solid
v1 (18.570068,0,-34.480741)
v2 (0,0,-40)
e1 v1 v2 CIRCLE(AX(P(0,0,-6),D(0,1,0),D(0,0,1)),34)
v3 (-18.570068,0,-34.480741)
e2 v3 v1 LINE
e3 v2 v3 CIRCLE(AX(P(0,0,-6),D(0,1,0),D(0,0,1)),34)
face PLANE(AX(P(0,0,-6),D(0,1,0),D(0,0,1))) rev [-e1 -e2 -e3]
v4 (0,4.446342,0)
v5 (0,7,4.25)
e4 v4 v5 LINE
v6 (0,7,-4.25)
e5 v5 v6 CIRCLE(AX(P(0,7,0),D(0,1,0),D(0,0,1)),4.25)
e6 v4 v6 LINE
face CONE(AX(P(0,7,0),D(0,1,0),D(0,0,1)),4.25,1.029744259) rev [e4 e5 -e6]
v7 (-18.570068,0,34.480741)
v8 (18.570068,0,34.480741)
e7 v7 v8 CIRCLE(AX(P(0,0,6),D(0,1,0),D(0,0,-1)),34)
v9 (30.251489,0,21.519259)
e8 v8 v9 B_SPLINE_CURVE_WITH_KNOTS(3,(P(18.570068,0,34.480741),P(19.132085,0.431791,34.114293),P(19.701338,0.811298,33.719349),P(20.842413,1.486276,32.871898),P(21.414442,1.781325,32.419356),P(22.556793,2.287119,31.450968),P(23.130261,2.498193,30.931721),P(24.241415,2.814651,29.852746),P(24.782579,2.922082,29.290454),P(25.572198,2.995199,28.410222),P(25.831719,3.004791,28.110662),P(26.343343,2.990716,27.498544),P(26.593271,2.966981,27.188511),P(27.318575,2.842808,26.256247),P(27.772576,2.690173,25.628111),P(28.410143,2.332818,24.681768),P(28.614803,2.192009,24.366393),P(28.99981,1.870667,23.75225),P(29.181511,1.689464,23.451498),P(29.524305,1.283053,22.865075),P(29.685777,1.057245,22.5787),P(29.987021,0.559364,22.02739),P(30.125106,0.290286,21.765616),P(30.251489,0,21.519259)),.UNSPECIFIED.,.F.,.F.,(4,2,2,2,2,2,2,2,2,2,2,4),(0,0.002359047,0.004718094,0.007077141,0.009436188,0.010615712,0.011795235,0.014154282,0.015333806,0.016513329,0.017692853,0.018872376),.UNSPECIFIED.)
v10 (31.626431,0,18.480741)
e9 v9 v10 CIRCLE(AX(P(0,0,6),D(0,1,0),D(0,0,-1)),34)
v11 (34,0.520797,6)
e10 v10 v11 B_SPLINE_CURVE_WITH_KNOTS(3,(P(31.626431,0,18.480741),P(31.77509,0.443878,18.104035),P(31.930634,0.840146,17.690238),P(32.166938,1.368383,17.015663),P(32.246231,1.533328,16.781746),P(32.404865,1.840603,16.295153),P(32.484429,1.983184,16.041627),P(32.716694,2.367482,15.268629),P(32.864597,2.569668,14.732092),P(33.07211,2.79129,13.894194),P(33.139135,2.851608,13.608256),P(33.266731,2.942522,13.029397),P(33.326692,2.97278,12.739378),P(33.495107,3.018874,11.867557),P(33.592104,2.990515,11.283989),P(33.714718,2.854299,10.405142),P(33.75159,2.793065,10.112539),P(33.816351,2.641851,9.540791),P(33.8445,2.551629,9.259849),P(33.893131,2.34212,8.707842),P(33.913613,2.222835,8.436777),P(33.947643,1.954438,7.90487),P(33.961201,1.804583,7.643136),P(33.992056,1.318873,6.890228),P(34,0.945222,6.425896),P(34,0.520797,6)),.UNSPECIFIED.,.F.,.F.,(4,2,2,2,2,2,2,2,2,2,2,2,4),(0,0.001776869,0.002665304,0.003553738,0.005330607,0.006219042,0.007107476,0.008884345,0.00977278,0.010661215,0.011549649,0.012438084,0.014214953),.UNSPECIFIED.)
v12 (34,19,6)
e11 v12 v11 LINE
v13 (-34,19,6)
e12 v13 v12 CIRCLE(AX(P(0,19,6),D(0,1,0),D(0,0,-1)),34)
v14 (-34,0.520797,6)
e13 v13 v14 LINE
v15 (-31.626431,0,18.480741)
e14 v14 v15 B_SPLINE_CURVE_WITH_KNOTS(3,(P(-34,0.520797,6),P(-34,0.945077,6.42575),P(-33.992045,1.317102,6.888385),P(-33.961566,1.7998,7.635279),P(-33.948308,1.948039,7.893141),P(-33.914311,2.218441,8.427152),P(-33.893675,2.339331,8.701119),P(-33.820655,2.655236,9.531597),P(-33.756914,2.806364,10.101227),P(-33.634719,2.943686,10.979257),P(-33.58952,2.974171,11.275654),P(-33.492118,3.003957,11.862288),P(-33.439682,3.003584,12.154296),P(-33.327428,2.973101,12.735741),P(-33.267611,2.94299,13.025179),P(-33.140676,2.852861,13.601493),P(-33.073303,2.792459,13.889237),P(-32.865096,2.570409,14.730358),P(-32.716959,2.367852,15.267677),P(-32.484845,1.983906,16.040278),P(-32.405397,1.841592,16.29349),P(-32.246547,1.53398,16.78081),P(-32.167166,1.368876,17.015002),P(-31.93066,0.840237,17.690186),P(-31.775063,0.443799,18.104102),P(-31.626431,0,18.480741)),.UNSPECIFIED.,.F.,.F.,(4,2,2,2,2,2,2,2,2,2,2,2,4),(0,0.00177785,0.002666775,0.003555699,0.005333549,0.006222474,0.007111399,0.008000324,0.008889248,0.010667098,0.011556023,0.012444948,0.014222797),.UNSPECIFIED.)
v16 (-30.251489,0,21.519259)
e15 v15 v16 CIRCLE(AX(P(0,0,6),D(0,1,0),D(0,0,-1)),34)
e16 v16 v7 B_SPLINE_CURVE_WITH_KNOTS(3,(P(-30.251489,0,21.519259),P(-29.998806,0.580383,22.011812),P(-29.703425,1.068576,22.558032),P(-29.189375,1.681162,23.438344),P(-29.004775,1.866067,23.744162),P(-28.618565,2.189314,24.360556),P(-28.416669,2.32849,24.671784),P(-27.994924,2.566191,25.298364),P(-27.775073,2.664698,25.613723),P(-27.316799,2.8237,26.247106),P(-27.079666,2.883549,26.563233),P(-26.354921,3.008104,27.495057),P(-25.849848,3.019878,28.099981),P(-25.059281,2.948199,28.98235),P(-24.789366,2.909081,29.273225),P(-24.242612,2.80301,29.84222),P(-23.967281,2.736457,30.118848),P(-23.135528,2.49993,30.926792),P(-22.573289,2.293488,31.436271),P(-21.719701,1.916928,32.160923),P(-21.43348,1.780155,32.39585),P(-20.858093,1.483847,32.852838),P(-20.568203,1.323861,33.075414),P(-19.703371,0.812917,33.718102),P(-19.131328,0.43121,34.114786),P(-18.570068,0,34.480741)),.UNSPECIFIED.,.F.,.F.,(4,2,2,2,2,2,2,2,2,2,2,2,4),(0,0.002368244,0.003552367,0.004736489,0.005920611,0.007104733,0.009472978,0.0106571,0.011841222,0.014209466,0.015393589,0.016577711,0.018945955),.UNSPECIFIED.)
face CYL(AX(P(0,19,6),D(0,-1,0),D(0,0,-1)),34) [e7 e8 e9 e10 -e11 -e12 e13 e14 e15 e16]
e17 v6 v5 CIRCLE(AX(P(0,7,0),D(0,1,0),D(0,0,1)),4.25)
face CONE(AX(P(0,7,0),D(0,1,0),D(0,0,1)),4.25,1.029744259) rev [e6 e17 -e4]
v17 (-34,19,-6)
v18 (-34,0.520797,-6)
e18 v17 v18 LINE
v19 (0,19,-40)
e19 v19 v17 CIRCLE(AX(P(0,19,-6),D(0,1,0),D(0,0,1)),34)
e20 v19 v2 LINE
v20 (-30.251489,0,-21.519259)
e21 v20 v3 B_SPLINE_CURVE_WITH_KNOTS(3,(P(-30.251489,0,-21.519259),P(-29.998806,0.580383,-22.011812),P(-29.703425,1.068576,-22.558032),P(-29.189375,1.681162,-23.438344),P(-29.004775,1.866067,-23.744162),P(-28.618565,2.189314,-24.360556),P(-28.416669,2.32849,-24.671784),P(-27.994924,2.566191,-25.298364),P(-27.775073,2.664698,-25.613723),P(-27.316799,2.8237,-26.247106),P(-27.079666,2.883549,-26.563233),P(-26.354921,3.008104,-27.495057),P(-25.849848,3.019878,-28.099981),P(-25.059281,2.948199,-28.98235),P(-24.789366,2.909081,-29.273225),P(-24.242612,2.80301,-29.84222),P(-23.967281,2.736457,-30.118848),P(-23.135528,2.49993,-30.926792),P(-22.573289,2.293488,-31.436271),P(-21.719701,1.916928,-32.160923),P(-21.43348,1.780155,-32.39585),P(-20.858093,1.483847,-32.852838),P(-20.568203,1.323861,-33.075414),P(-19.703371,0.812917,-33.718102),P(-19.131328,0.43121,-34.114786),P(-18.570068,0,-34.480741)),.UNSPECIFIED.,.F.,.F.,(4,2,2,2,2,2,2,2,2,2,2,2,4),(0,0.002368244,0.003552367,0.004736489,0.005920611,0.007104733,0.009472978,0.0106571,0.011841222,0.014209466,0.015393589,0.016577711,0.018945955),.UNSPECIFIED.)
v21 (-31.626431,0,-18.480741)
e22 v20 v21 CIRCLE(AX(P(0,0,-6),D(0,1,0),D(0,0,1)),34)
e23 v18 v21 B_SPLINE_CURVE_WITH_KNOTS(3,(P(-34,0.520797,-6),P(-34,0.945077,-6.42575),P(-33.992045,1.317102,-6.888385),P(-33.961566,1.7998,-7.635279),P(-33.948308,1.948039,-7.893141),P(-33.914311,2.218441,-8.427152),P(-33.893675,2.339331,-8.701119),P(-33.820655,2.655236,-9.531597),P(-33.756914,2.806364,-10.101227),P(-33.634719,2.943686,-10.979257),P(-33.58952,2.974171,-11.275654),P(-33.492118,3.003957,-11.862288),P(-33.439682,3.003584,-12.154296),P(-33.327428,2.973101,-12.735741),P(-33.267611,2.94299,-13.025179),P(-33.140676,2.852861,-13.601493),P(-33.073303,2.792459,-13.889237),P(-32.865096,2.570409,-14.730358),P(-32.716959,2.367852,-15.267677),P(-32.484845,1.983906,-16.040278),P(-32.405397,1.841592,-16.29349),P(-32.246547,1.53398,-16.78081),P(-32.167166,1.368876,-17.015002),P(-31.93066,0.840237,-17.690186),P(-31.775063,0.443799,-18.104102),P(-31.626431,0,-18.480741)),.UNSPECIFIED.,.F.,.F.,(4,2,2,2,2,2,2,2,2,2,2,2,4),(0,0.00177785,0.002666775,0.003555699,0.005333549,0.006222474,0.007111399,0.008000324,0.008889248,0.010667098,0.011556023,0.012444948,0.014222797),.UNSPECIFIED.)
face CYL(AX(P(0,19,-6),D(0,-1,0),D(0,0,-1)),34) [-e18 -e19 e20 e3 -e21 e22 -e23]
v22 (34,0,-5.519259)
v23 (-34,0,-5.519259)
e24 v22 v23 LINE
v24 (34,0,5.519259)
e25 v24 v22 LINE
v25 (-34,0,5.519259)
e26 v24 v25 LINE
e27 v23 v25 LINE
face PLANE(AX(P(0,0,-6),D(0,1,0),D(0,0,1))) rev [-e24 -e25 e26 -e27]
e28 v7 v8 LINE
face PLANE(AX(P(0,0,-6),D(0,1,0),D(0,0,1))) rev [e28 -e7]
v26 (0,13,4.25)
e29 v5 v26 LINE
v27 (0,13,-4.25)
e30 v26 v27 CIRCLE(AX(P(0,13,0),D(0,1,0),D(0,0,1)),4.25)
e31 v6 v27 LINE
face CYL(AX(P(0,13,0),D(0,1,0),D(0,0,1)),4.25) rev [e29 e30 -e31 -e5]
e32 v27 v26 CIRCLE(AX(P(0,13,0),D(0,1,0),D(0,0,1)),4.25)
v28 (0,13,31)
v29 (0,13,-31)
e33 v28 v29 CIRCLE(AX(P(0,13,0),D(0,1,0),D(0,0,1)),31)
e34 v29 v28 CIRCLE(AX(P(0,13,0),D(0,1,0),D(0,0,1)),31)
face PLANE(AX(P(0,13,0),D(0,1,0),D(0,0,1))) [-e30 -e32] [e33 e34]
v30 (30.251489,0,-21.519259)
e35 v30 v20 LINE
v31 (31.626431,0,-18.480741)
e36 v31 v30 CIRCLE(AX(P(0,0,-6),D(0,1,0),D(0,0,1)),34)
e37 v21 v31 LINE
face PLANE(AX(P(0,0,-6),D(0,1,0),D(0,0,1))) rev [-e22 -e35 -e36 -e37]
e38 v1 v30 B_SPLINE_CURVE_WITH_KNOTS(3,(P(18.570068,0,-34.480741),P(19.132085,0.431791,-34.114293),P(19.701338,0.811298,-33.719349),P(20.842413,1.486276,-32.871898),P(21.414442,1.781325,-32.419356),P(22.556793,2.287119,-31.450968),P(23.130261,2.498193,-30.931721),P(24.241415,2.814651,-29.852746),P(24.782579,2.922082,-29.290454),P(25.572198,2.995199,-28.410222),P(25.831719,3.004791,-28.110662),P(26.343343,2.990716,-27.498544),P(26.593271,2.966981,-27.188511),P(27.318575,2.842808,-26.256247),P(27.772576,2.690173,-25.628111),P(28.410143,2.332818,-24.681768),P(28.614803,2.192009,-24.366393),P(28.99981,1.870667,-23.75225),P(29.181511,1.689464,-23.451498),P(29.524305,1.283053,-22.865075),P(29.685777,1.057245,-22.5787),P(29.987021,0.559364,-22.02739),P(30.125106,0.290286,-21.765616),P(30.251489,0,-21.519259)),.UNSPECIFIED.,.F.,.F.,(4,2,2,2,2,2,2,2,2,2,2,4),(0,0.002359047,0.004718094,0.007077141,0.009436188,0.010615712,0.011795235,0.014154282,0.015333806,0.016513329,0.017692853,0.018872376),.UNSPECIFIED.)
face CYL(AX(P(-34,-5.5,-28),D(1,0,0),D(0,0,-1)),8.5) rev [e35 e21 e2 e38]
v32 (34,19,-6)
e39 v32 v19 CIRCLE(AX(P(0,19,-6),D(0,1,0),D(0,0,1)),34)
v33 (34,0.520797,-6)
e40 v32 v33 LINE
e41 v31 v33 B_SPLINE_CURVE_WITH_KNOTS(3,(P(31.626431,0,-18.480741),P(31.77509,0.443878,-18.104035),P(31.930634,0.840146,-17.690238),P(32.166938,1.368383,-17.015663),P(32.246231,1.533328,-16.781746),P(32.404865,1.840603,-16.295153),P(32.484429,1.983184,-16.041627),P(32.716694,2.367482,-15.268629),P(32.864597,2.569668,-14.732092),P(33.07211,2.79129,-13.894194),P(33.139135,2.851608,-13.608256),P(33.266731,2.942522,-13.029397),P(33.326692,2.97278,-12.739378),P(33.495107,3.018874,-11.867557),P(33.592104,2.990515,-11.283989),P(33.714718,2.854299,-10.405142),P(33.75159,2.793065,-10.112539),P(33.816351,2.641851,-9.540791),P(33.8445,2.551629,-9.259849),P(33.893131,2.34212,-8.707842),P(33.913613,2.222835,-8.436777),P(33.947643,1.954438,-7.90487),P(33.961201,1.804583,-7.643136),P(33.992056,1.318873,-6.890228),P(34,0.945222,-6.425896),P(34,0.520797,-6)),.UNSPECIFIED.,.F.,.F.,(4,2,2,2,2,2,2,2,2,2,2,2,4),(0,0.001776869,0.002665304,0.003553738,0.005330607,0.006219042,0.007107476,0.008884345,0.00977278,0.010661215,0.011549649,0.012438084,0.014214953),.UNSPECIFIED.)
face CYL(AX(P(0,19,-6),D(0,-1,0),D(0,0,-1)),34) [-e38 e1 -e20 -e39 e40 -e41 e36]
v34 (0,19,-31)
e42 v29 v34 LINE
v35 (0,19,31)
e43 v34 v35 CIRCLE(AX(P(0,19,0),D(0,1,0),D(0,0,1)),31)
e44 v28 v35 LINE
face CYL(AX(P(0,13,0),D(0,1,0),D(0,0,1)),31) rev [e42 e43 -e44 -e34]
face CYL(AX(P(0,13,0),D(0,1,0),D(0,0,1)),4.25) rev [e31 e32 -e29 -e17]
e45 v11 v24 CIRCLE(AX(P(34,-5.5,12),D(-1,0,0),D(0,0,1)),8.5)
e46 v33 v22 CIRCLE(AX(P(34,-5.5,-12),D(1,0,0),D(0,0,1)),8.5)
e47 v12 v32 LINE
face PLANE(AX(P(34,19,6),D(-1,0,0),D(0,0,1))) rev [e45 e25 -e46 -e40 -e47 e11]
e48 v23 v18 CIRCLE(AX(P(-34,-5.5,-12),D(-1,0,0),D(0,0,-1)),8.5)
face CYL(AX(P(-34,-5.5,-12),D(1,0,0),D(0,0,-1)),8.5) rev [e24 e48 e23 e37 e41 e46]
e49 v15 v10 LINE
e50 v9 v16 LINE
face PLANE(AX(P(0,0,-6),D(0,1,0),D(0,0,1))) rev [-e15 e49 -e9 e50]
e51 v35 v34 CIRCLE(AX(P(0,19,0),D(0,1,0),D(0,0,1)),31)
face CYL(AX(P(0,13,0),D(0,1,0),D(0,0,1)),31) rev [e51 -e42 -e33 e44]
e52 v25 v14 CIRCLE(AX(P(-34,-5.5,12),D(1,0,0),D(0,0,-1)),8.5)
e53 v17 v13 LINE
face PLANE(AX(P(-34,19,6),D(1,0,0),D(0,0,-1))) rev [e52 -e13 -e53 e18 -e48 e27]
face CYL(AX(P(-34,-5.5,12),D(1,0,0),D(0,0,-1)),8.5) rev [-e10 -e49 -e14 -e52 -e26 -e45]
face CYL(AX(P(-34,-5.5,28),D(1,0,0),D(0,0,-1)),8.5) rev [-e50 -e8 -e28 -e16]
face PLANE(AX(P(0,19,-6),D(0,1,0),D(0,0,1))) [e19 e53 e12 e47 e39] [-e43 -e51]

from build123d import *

# Parameters (mm, degrees)
EXTRUDE_1_DEPTH          = 19
SKETCH_2_R               = 31
CUT_EXTRUDE_1_DEPTH      = 6
HOLE_WIZARD_M10_1_D      = 8.5
HOLE_WIZARD_M10_1_DEPTH  = 6
HOLE_WIZARD_M10_1_TIP    = 2.553657631
CUT_EXTRUDE_2_DEPTH      = 56.830099409
CUT_EXTRUDE_2_DEPTH_BACK = 56.830099409
SKETCH_5_R               = 8.5


with BuildPart() as part:
    # 草图1 → 凸台-拉伸1 (new body)
    with BuildSketch(Plane(origin=(0, 0, 0), x_dir=(1, 0, 0), z_dir=(0, 1, 0))):
        with BuildLine():
            Line((34, -6), (34, 6))
            ThreePointArc((34, 6), (0, 40), (-34, 6))
            Line((-34, 6), (-34, -6))
            ThreePointArc((-34, -6), (0, -40), (34, -6))
        make_face()
    extrude(amount=EXTRUDE_1_DEPTH)

    # 草图2 → 切除-拉伸1 (cut)
    with BuildSketch(Plane(origin=(0, 19, 0), x_dir=(1, 0, 0), z_dir=(0, 1, 0))):
        with Locations(Location((0, 0, 0), (0, 0, 270))):
            Circle(SKETCH_2_R)
    extrude(amount=-CUT_EXTRUDE_1_DEPTH, mode=Mode.SUBTRACT)

    # M10 螺纹孔1
    with Locations(Plane(origin=(0, 13, 0), x_dir=(1, 0, 0), z_dir=(0, 1, 0))):
        with Locations((0, 0)):
            Hole(HOLE_WIZARD_M10_1_D / 2, depth=HOLE_WIZARD_M10_1_DEPTH)
            with Locations((0, 0, -(HOLE_WIZARD_M10_1_DEPTH + HOLE_WIZARD_M10_1_TIP / 2))):  # 118° drill point
                Cone(0, HOLE_WIZARD_M10_1_D / 2, HOLE_WIZARD_M10_1_TIP, mode=Mode.SUBTRACT)

    # 草图5 → 切除-拉伸2 (cut, two sides: drawn at the far end of the back side and taken through both)
    with BuildSketch(Plane(origin=(0, 0, 0), x_dir=(0, 0, -1), z_dir=(1, 0, 0)).offset(-CUT_EXTRUDE_2_DEPTH_BACK)):
        with Locations((28, -5.5)):
            Circle(SKETCH_5_R)
        with Locations((12, -5.5)):
            Circle(SKETCH_5_R)
        with Locations((12, -5.5)):
            Circle(SKETCH_5_R)
        with Locations((28, -5.5)):
            Circle(SKETCH_5_R)
        with Locations((-28, -5.5)):
            Circle(SKETCH_5_R)
        with Locations((-12, -5.5)):
            Circle(SKETCH_5_R)
        with Locations((-12, -5.5)):
            Circle(SKETCH_5_R)
        with Locations((-28, -5.5)):
            Circle(SKETCH_5_R)
    extrude(amount=CUT_EXTRUDE_2_DEPTH + CUT_EXTRUDE_2_DEPTH_BACK, mode=Mode.SUBTRACT)


solid = part.part
